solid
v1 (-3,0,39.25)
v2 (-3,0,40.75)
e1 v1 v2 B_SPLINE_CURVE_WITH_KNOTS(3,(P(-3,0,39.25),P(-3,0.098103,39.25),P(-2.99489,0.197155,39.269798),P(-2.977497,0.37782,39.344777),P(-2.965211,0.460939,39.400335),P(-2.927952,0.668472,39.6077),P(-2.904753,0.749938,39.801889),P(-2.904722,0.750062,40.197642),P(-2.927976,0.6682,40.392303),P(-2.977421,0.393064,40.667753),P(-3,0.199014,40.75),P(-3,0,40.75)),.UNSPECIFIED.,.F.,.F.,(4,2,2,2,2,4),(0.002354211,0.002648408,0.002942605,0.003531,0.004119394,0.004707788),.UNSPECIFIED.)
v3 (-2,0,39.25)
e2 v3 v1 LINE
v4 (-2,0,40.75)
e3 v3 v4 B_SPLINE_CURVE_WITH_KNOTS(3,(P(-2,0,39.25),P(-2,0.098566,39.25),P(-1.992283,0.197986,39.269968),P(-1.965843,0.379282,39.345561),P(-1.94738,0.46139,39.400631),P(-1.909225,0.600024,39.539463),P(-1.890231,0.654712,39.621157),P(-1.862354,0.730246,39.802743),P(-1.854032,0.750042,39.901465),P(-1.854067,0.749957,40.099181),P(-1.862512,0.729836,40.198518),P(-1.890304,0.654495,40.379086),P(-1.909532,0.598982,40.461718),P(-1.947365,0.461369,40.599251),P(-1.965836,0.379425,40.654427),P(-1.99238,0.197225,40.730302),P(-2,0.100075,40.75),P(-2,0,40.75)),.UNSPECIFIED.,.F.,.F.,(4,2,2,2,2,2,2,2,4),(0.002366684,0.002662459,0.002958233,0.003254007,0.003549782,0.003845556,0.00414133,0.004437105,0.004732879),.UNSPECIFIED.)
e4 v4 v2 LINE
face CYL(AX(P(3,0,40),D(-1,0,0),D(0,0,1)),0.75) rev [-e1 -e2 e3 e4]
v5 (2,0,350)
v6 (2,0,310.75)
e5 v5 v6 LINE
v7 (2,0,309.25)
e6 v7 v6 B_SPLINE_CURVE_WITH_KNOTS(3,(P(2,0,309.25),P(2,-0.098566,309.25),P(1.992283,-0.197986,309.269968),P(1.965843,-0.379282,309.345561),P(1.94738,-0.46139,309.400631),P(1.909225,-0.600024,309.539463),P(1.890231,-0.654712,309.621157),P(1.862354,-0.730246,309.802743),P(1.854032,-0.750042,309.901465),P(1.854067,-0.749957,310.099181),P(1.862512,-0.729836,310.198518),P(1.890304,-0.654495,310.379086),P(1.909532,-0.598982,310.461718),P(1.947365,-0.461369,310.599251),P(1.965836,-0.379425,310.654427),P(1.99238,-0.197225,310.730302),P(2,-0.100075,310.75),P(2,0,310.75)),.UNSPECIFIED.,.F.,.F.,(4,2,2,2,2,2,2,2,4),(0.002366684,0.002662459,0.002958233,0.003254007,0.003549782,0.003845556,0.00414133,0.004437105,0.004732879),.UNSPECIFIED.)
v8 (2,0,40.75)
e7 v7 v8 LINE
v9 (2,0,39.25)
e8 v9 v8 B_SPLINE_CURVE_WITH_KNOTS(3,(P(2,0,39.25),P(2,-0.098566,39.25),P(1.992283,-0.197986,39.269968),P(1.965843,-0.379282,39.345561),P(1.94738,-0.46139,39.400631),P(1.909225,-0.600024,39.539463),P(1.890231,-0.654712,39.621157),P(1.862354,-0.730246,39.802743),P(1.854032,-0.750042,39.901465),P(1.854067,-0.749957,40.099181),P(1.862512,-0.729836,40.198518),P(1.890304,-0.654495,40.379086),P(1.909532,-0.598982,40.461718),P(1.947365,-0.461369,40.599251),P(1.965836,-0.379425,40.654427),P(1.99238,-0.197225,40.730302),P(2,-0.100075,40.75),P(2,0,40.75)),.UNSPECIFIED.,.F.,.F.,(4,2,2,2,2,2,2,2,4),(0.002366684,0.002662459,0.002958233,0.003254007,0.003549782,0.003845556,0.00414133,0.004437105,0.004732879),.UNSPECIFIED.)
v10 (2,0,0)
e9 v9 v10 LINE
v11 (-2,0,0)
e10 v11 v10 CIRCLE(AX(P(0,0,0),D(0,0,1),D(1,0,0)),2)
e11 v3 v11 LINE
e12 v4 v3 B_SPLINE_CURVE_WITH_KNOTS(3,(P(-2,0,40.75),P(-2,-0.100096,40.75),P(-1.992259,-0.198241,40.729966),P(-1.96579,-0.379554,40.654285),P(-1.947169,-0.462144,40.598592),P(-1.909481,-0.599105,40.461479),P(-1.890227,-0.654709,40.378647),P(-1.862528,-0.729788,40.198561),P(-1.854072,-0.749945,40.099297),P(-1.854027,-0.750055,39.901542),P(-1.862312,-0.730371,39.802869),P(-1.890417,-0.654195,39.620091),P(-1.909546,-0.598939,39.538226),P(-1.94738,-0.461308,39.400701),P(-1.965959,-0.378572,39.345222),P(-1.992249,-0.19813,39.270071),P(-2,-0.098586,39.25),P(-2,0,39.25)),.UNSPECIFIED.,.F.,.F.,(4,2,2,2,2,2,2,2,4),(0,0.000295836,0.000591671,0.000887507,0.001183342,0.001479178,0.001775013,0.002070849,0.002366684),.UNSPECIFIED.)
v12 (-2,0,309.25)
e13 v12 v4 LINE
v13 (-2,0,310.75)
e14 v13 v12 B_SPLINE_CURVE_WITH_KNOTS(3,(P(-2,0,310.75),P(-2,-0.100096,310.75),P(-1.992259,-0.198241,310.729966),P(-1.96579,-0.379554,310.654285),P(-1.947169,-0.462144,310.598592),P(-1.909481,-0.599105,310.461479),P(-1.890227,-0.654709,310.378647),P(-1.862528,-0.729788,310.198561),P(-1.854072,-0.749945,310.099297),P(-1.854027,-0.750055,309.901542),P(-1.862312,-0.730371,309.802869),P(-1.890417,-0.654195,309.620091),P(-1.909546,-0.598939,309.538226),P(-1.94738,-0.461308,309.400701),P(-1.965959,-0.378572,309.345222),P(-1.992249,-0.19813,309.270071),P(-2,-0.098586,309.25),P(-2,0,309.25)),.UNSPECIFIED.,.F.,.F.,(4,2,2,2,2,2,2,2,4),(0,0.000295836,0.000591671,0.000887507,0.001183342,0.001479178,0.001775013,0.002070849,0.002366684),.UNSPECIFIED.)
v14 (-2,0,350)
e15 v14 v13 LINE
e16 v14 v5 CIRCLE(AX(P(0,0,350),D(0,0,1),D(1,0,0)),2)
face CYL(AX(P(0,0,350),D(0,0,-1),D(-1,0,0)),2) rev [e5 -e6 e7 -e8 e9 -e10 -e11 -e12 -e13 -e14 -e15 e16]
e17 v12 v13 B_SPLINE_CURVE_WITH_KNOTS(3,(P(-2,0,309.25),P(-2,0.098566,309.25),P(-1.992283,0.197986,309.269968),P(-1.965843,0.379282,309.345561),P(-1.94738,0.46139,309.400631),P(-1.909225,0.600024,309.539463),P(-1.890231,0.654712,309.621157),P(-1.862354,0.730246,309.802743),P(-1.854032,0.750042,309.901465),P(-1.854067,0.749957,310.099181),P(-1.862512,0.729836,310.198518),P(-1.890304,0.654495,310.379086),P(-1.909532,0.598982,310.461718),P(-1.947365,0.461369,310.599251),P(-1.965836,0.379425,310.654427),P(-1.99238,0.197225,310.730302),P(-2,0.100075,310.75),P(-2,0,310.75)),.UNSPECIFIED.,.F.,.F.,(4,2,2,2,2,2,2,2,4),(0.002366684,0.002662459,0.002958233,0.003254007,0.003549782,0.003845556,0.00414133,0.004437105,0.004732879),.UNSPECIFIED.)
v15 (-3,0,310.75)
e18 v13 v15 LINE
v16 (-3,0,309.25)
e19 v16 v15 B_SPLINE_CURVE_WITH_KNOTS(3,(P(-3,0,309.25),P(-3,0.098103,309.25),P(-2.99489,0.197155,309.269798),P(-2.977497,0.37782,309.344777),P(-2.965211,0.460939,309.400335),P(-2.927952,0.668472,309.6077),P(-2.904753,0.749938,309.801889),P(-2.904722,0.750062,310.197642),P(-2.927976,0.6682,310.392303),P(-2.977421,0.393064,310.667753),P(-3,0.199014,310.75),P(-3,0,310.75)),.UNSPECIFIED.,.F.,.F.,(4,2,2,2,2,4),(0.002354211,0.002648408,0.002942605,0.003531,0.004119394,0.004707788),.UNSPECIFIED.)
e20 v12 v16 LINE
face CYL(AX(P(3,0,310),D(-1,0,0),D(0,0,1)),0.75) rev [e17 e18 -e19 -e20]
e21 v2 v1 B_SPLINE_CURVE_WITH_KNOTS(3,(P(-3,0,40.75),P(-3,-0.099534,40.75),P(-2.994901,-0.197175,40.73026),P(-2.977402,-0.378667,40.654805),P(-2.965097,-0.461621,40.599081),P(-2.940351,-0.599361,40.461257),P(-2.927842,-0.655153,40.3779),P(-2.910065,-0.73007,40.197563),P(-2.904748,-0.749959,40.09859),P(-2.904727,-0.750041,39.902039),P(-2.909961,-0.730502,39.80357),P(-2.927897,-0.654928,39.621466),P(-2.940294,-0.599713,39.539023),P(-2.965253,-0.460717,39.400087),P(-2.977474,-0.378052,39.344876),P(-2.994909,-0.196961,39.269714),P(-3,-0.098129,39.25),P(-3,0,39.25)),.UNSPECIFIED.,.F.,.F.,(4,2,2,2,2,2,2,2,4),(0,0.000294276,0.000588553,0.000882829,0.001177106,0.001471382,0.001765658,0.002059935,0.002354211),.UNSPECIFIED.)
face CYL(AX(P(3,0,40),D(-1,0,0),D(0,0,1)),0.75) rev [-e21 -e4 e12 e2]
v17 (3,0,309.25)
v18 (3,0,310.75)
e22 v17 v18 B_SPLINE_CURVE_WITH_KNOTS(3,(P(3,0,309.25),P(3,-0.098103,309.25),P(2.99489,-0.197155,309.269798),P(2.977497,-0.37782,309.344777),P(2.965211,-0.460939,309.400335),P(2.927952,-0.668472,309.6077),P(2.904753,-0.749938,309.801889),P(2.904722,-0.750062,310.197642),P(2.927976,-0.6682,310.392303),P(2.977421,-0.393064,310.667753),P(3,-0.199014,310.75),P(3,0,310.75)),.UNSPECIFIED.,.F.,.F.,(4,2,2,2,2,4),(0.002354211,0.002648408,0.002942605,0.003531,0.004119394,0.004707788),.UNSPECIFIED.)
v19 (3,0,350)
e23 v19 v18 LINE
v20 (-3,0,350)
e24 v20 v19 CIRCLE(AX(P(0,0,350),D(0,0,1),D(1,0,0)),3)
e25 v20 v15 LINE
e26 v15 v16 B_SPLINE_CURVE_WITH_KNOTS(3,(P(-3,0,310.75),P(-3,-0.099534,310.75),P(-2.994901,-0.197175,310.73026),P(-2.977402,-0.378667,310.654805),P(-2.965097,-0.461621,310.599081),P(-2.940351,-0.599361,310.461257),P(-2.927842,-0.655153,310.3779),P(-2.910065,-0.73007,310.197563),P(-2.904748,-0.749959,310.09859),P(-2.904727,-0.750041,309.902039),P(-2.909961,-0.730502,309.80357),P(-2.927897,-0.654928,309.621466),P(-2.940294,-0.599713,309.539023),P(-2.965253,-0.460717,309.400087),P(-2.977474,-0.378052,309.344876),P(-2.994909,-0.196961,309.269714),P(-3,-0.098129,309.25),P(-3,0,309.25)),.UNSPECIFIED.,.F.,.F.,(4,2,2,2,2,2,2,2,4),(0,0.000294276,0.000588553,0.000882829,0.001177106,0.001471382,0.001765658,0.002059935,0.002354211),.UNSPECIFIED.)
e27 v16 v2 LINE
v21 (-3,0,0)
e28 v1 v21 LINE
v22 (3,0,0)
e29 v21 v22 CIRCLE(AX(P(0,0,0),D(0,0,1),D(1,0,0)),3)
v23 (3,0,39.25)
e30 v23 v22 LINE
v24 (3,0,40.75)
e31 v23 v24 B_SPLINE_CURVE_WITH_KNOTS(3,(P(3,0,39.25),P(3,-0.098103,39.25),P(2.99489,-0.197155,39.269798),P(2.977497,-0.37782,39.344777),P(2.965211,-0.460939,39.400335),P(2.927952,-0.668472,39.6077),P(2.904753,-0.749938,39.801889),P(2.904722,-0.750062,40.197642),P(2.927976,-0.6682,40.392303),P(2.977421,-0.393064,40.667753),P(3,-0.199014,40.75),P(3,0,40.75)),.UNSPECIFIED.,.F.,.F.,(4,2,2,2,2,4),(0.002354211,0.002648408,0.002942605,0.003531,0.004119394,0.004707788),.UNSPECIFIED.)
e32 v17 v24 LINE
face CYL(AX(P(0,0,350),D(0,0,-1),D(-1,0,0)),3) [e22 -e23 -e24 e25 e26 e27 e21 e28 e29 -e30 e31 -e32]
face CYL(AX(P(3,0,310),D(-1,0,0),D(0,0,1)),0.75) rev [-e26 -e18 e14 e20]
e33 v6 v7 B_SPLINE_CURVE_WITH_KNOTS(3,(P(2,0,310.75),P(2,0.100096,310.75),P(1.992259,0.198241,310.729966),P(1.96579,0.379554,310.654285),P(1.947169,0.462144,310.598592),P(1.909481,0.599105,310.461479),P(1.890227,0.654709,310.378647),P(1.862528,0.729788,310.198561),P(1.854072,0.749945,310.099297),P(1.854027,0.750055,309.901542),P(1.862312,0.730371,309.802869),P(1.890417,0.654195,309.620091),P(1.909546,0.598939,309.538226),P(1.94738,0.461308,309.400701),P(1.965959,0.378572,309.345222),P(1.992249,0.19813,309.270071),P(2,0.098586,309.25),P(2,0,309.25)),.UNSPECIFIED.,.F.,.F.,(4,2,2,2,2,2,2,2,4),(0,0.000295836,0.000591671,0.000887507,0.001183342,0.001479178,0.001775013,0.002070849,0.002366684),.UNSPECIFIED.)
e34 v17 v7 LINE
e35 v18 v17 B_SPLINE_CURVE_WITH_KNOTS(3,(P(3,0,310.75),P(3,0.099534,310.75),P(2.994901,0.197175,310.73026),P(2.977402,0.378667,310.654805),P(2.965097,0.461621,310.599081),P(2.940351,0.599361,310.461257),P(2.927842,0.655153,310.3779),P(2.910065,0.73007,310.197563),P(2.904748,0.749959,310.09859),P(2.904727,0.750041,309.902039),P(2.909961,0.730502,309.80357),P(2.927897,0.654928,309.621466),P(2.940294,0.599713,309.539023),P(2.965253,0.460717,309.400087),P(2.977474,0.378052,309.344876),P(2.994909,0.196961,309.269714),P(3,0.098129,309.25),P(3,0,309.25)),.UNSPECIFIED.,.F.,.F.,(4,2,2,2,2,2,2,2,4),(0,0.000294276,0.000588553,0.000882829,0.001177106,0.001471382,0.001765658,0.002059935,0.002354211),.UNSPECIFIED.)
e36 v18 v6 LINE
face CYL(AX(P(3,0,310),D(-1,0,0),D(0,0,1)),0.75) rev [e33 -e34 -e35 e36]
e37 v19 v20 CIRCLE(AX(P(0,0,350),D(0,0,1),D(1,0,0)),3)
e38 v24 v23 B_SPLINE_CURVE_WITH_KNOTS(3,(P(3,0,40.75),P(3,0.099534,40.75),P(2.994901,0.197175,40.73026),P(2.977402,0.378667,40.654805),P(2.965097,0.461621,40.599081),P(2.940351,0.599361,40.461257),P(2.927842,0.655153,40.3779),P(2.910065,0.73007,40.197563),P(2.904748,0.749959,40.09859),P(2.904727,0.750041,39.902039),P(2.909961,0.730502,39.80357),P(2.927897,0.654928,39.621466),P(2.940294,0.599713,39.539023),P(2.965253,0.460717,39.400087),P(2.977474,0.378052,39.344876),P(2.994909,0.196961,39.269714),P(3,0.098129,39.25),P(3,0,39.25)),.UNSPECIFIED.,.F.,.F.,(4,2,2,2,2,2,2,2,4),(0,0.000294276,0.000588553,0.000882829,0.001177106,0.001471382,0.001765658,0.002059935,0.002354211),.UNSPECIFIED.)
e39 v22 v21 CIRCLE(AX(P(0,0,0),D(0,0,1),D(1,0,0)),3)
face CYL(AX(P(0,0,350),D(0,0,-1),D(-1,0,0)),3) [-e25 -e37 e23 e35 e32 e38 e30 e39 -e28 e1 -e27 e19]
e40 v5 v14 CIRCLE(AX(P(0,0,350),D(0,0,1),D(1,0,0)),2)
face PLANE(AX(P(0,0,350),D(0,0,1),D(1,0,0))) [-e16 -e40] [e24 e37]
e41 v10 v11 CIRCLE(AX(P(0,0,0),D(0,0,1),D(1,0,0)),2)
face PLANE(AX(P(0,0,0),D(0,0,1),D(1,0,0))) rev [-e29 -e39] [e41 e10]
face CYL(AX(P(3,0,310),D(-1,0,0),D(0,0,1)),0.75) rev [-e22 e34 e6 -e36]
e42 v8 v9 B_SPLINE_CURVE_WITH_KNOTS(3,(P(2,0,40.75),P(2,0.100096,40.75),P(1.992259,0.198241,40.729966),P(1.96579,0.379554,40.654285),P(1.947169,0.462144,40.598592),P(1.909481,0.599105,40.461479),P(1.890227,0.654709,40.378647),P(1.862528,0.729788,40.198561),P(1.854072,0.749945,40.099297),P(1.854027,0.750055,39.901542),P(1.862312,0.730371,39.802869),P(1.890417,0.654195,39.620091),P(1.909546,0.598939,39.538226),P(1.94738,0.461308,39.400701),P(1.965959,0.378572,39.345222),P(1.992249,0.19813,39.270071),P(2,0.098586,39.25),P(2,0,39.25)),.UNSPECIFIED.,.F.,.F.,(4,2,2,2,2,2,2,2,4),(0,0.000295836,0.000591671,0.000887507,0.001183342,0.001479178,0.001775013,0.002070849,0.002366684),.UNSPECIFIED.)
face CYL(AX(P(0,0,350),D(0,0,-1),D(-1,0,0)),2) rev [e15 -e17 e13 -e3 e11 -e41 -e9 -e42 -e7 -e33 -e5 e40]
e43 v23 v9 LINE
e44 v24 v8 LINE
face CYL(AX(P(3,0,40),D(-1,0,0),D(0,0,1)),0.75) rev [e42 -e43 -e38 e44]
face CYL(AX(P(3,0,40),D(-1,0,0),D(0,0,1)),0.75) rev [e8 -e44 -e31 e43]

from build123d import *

# Parameters (mm, degrees)
SKETCH1_R               = 3
SKETCH1_R_2             = 2
BOSS_EXTRUDE1_DEPTH     = 350
CUT_EXTRUDE1_DEPTH      = 351.025713341
CUT_EXTRUDE1_DEPTH_BACK = 351.025713341
SKETCH3_R               = 0.75


with BuildPart() as part:
    # Sketch1 → Boss-Extrude1 (new body)
    with BuildSketch(Plane.XY):
        Circle(SKETCH1_R)
        Circle(SKETCH1_R_2, mode=Mode.SUBTRACT)
    extrude(amount=BOSS_EXTRUDE1_DEPTH)

    # Sketch3 → Cut-Extrude1 (cut, two sides: drawn at the far end of the back side and taken through both)
    with BuildSketch(Plane(origin=(0, 0, 0), x_dir=(0, 1, 0), z_dir=(-1, 0, 0)).offset(-CUT_EXTRUDE1_DEPTH_BACK)):
        with Locations(Location((0, -40, 0), (0, 0, 270))):
            Circle(SKETCH3_R)
        with Locations(Location((0, -310, 0), (0, 0, 270))):
            Circle(SKETCH3_R)
    extrude(amount=CUT_EXTRUDE1_DEPTH + CUT_EXTRUDE1_DEPTH_BACK, mode=Mode.SUBTRACT)


solid = part.part
